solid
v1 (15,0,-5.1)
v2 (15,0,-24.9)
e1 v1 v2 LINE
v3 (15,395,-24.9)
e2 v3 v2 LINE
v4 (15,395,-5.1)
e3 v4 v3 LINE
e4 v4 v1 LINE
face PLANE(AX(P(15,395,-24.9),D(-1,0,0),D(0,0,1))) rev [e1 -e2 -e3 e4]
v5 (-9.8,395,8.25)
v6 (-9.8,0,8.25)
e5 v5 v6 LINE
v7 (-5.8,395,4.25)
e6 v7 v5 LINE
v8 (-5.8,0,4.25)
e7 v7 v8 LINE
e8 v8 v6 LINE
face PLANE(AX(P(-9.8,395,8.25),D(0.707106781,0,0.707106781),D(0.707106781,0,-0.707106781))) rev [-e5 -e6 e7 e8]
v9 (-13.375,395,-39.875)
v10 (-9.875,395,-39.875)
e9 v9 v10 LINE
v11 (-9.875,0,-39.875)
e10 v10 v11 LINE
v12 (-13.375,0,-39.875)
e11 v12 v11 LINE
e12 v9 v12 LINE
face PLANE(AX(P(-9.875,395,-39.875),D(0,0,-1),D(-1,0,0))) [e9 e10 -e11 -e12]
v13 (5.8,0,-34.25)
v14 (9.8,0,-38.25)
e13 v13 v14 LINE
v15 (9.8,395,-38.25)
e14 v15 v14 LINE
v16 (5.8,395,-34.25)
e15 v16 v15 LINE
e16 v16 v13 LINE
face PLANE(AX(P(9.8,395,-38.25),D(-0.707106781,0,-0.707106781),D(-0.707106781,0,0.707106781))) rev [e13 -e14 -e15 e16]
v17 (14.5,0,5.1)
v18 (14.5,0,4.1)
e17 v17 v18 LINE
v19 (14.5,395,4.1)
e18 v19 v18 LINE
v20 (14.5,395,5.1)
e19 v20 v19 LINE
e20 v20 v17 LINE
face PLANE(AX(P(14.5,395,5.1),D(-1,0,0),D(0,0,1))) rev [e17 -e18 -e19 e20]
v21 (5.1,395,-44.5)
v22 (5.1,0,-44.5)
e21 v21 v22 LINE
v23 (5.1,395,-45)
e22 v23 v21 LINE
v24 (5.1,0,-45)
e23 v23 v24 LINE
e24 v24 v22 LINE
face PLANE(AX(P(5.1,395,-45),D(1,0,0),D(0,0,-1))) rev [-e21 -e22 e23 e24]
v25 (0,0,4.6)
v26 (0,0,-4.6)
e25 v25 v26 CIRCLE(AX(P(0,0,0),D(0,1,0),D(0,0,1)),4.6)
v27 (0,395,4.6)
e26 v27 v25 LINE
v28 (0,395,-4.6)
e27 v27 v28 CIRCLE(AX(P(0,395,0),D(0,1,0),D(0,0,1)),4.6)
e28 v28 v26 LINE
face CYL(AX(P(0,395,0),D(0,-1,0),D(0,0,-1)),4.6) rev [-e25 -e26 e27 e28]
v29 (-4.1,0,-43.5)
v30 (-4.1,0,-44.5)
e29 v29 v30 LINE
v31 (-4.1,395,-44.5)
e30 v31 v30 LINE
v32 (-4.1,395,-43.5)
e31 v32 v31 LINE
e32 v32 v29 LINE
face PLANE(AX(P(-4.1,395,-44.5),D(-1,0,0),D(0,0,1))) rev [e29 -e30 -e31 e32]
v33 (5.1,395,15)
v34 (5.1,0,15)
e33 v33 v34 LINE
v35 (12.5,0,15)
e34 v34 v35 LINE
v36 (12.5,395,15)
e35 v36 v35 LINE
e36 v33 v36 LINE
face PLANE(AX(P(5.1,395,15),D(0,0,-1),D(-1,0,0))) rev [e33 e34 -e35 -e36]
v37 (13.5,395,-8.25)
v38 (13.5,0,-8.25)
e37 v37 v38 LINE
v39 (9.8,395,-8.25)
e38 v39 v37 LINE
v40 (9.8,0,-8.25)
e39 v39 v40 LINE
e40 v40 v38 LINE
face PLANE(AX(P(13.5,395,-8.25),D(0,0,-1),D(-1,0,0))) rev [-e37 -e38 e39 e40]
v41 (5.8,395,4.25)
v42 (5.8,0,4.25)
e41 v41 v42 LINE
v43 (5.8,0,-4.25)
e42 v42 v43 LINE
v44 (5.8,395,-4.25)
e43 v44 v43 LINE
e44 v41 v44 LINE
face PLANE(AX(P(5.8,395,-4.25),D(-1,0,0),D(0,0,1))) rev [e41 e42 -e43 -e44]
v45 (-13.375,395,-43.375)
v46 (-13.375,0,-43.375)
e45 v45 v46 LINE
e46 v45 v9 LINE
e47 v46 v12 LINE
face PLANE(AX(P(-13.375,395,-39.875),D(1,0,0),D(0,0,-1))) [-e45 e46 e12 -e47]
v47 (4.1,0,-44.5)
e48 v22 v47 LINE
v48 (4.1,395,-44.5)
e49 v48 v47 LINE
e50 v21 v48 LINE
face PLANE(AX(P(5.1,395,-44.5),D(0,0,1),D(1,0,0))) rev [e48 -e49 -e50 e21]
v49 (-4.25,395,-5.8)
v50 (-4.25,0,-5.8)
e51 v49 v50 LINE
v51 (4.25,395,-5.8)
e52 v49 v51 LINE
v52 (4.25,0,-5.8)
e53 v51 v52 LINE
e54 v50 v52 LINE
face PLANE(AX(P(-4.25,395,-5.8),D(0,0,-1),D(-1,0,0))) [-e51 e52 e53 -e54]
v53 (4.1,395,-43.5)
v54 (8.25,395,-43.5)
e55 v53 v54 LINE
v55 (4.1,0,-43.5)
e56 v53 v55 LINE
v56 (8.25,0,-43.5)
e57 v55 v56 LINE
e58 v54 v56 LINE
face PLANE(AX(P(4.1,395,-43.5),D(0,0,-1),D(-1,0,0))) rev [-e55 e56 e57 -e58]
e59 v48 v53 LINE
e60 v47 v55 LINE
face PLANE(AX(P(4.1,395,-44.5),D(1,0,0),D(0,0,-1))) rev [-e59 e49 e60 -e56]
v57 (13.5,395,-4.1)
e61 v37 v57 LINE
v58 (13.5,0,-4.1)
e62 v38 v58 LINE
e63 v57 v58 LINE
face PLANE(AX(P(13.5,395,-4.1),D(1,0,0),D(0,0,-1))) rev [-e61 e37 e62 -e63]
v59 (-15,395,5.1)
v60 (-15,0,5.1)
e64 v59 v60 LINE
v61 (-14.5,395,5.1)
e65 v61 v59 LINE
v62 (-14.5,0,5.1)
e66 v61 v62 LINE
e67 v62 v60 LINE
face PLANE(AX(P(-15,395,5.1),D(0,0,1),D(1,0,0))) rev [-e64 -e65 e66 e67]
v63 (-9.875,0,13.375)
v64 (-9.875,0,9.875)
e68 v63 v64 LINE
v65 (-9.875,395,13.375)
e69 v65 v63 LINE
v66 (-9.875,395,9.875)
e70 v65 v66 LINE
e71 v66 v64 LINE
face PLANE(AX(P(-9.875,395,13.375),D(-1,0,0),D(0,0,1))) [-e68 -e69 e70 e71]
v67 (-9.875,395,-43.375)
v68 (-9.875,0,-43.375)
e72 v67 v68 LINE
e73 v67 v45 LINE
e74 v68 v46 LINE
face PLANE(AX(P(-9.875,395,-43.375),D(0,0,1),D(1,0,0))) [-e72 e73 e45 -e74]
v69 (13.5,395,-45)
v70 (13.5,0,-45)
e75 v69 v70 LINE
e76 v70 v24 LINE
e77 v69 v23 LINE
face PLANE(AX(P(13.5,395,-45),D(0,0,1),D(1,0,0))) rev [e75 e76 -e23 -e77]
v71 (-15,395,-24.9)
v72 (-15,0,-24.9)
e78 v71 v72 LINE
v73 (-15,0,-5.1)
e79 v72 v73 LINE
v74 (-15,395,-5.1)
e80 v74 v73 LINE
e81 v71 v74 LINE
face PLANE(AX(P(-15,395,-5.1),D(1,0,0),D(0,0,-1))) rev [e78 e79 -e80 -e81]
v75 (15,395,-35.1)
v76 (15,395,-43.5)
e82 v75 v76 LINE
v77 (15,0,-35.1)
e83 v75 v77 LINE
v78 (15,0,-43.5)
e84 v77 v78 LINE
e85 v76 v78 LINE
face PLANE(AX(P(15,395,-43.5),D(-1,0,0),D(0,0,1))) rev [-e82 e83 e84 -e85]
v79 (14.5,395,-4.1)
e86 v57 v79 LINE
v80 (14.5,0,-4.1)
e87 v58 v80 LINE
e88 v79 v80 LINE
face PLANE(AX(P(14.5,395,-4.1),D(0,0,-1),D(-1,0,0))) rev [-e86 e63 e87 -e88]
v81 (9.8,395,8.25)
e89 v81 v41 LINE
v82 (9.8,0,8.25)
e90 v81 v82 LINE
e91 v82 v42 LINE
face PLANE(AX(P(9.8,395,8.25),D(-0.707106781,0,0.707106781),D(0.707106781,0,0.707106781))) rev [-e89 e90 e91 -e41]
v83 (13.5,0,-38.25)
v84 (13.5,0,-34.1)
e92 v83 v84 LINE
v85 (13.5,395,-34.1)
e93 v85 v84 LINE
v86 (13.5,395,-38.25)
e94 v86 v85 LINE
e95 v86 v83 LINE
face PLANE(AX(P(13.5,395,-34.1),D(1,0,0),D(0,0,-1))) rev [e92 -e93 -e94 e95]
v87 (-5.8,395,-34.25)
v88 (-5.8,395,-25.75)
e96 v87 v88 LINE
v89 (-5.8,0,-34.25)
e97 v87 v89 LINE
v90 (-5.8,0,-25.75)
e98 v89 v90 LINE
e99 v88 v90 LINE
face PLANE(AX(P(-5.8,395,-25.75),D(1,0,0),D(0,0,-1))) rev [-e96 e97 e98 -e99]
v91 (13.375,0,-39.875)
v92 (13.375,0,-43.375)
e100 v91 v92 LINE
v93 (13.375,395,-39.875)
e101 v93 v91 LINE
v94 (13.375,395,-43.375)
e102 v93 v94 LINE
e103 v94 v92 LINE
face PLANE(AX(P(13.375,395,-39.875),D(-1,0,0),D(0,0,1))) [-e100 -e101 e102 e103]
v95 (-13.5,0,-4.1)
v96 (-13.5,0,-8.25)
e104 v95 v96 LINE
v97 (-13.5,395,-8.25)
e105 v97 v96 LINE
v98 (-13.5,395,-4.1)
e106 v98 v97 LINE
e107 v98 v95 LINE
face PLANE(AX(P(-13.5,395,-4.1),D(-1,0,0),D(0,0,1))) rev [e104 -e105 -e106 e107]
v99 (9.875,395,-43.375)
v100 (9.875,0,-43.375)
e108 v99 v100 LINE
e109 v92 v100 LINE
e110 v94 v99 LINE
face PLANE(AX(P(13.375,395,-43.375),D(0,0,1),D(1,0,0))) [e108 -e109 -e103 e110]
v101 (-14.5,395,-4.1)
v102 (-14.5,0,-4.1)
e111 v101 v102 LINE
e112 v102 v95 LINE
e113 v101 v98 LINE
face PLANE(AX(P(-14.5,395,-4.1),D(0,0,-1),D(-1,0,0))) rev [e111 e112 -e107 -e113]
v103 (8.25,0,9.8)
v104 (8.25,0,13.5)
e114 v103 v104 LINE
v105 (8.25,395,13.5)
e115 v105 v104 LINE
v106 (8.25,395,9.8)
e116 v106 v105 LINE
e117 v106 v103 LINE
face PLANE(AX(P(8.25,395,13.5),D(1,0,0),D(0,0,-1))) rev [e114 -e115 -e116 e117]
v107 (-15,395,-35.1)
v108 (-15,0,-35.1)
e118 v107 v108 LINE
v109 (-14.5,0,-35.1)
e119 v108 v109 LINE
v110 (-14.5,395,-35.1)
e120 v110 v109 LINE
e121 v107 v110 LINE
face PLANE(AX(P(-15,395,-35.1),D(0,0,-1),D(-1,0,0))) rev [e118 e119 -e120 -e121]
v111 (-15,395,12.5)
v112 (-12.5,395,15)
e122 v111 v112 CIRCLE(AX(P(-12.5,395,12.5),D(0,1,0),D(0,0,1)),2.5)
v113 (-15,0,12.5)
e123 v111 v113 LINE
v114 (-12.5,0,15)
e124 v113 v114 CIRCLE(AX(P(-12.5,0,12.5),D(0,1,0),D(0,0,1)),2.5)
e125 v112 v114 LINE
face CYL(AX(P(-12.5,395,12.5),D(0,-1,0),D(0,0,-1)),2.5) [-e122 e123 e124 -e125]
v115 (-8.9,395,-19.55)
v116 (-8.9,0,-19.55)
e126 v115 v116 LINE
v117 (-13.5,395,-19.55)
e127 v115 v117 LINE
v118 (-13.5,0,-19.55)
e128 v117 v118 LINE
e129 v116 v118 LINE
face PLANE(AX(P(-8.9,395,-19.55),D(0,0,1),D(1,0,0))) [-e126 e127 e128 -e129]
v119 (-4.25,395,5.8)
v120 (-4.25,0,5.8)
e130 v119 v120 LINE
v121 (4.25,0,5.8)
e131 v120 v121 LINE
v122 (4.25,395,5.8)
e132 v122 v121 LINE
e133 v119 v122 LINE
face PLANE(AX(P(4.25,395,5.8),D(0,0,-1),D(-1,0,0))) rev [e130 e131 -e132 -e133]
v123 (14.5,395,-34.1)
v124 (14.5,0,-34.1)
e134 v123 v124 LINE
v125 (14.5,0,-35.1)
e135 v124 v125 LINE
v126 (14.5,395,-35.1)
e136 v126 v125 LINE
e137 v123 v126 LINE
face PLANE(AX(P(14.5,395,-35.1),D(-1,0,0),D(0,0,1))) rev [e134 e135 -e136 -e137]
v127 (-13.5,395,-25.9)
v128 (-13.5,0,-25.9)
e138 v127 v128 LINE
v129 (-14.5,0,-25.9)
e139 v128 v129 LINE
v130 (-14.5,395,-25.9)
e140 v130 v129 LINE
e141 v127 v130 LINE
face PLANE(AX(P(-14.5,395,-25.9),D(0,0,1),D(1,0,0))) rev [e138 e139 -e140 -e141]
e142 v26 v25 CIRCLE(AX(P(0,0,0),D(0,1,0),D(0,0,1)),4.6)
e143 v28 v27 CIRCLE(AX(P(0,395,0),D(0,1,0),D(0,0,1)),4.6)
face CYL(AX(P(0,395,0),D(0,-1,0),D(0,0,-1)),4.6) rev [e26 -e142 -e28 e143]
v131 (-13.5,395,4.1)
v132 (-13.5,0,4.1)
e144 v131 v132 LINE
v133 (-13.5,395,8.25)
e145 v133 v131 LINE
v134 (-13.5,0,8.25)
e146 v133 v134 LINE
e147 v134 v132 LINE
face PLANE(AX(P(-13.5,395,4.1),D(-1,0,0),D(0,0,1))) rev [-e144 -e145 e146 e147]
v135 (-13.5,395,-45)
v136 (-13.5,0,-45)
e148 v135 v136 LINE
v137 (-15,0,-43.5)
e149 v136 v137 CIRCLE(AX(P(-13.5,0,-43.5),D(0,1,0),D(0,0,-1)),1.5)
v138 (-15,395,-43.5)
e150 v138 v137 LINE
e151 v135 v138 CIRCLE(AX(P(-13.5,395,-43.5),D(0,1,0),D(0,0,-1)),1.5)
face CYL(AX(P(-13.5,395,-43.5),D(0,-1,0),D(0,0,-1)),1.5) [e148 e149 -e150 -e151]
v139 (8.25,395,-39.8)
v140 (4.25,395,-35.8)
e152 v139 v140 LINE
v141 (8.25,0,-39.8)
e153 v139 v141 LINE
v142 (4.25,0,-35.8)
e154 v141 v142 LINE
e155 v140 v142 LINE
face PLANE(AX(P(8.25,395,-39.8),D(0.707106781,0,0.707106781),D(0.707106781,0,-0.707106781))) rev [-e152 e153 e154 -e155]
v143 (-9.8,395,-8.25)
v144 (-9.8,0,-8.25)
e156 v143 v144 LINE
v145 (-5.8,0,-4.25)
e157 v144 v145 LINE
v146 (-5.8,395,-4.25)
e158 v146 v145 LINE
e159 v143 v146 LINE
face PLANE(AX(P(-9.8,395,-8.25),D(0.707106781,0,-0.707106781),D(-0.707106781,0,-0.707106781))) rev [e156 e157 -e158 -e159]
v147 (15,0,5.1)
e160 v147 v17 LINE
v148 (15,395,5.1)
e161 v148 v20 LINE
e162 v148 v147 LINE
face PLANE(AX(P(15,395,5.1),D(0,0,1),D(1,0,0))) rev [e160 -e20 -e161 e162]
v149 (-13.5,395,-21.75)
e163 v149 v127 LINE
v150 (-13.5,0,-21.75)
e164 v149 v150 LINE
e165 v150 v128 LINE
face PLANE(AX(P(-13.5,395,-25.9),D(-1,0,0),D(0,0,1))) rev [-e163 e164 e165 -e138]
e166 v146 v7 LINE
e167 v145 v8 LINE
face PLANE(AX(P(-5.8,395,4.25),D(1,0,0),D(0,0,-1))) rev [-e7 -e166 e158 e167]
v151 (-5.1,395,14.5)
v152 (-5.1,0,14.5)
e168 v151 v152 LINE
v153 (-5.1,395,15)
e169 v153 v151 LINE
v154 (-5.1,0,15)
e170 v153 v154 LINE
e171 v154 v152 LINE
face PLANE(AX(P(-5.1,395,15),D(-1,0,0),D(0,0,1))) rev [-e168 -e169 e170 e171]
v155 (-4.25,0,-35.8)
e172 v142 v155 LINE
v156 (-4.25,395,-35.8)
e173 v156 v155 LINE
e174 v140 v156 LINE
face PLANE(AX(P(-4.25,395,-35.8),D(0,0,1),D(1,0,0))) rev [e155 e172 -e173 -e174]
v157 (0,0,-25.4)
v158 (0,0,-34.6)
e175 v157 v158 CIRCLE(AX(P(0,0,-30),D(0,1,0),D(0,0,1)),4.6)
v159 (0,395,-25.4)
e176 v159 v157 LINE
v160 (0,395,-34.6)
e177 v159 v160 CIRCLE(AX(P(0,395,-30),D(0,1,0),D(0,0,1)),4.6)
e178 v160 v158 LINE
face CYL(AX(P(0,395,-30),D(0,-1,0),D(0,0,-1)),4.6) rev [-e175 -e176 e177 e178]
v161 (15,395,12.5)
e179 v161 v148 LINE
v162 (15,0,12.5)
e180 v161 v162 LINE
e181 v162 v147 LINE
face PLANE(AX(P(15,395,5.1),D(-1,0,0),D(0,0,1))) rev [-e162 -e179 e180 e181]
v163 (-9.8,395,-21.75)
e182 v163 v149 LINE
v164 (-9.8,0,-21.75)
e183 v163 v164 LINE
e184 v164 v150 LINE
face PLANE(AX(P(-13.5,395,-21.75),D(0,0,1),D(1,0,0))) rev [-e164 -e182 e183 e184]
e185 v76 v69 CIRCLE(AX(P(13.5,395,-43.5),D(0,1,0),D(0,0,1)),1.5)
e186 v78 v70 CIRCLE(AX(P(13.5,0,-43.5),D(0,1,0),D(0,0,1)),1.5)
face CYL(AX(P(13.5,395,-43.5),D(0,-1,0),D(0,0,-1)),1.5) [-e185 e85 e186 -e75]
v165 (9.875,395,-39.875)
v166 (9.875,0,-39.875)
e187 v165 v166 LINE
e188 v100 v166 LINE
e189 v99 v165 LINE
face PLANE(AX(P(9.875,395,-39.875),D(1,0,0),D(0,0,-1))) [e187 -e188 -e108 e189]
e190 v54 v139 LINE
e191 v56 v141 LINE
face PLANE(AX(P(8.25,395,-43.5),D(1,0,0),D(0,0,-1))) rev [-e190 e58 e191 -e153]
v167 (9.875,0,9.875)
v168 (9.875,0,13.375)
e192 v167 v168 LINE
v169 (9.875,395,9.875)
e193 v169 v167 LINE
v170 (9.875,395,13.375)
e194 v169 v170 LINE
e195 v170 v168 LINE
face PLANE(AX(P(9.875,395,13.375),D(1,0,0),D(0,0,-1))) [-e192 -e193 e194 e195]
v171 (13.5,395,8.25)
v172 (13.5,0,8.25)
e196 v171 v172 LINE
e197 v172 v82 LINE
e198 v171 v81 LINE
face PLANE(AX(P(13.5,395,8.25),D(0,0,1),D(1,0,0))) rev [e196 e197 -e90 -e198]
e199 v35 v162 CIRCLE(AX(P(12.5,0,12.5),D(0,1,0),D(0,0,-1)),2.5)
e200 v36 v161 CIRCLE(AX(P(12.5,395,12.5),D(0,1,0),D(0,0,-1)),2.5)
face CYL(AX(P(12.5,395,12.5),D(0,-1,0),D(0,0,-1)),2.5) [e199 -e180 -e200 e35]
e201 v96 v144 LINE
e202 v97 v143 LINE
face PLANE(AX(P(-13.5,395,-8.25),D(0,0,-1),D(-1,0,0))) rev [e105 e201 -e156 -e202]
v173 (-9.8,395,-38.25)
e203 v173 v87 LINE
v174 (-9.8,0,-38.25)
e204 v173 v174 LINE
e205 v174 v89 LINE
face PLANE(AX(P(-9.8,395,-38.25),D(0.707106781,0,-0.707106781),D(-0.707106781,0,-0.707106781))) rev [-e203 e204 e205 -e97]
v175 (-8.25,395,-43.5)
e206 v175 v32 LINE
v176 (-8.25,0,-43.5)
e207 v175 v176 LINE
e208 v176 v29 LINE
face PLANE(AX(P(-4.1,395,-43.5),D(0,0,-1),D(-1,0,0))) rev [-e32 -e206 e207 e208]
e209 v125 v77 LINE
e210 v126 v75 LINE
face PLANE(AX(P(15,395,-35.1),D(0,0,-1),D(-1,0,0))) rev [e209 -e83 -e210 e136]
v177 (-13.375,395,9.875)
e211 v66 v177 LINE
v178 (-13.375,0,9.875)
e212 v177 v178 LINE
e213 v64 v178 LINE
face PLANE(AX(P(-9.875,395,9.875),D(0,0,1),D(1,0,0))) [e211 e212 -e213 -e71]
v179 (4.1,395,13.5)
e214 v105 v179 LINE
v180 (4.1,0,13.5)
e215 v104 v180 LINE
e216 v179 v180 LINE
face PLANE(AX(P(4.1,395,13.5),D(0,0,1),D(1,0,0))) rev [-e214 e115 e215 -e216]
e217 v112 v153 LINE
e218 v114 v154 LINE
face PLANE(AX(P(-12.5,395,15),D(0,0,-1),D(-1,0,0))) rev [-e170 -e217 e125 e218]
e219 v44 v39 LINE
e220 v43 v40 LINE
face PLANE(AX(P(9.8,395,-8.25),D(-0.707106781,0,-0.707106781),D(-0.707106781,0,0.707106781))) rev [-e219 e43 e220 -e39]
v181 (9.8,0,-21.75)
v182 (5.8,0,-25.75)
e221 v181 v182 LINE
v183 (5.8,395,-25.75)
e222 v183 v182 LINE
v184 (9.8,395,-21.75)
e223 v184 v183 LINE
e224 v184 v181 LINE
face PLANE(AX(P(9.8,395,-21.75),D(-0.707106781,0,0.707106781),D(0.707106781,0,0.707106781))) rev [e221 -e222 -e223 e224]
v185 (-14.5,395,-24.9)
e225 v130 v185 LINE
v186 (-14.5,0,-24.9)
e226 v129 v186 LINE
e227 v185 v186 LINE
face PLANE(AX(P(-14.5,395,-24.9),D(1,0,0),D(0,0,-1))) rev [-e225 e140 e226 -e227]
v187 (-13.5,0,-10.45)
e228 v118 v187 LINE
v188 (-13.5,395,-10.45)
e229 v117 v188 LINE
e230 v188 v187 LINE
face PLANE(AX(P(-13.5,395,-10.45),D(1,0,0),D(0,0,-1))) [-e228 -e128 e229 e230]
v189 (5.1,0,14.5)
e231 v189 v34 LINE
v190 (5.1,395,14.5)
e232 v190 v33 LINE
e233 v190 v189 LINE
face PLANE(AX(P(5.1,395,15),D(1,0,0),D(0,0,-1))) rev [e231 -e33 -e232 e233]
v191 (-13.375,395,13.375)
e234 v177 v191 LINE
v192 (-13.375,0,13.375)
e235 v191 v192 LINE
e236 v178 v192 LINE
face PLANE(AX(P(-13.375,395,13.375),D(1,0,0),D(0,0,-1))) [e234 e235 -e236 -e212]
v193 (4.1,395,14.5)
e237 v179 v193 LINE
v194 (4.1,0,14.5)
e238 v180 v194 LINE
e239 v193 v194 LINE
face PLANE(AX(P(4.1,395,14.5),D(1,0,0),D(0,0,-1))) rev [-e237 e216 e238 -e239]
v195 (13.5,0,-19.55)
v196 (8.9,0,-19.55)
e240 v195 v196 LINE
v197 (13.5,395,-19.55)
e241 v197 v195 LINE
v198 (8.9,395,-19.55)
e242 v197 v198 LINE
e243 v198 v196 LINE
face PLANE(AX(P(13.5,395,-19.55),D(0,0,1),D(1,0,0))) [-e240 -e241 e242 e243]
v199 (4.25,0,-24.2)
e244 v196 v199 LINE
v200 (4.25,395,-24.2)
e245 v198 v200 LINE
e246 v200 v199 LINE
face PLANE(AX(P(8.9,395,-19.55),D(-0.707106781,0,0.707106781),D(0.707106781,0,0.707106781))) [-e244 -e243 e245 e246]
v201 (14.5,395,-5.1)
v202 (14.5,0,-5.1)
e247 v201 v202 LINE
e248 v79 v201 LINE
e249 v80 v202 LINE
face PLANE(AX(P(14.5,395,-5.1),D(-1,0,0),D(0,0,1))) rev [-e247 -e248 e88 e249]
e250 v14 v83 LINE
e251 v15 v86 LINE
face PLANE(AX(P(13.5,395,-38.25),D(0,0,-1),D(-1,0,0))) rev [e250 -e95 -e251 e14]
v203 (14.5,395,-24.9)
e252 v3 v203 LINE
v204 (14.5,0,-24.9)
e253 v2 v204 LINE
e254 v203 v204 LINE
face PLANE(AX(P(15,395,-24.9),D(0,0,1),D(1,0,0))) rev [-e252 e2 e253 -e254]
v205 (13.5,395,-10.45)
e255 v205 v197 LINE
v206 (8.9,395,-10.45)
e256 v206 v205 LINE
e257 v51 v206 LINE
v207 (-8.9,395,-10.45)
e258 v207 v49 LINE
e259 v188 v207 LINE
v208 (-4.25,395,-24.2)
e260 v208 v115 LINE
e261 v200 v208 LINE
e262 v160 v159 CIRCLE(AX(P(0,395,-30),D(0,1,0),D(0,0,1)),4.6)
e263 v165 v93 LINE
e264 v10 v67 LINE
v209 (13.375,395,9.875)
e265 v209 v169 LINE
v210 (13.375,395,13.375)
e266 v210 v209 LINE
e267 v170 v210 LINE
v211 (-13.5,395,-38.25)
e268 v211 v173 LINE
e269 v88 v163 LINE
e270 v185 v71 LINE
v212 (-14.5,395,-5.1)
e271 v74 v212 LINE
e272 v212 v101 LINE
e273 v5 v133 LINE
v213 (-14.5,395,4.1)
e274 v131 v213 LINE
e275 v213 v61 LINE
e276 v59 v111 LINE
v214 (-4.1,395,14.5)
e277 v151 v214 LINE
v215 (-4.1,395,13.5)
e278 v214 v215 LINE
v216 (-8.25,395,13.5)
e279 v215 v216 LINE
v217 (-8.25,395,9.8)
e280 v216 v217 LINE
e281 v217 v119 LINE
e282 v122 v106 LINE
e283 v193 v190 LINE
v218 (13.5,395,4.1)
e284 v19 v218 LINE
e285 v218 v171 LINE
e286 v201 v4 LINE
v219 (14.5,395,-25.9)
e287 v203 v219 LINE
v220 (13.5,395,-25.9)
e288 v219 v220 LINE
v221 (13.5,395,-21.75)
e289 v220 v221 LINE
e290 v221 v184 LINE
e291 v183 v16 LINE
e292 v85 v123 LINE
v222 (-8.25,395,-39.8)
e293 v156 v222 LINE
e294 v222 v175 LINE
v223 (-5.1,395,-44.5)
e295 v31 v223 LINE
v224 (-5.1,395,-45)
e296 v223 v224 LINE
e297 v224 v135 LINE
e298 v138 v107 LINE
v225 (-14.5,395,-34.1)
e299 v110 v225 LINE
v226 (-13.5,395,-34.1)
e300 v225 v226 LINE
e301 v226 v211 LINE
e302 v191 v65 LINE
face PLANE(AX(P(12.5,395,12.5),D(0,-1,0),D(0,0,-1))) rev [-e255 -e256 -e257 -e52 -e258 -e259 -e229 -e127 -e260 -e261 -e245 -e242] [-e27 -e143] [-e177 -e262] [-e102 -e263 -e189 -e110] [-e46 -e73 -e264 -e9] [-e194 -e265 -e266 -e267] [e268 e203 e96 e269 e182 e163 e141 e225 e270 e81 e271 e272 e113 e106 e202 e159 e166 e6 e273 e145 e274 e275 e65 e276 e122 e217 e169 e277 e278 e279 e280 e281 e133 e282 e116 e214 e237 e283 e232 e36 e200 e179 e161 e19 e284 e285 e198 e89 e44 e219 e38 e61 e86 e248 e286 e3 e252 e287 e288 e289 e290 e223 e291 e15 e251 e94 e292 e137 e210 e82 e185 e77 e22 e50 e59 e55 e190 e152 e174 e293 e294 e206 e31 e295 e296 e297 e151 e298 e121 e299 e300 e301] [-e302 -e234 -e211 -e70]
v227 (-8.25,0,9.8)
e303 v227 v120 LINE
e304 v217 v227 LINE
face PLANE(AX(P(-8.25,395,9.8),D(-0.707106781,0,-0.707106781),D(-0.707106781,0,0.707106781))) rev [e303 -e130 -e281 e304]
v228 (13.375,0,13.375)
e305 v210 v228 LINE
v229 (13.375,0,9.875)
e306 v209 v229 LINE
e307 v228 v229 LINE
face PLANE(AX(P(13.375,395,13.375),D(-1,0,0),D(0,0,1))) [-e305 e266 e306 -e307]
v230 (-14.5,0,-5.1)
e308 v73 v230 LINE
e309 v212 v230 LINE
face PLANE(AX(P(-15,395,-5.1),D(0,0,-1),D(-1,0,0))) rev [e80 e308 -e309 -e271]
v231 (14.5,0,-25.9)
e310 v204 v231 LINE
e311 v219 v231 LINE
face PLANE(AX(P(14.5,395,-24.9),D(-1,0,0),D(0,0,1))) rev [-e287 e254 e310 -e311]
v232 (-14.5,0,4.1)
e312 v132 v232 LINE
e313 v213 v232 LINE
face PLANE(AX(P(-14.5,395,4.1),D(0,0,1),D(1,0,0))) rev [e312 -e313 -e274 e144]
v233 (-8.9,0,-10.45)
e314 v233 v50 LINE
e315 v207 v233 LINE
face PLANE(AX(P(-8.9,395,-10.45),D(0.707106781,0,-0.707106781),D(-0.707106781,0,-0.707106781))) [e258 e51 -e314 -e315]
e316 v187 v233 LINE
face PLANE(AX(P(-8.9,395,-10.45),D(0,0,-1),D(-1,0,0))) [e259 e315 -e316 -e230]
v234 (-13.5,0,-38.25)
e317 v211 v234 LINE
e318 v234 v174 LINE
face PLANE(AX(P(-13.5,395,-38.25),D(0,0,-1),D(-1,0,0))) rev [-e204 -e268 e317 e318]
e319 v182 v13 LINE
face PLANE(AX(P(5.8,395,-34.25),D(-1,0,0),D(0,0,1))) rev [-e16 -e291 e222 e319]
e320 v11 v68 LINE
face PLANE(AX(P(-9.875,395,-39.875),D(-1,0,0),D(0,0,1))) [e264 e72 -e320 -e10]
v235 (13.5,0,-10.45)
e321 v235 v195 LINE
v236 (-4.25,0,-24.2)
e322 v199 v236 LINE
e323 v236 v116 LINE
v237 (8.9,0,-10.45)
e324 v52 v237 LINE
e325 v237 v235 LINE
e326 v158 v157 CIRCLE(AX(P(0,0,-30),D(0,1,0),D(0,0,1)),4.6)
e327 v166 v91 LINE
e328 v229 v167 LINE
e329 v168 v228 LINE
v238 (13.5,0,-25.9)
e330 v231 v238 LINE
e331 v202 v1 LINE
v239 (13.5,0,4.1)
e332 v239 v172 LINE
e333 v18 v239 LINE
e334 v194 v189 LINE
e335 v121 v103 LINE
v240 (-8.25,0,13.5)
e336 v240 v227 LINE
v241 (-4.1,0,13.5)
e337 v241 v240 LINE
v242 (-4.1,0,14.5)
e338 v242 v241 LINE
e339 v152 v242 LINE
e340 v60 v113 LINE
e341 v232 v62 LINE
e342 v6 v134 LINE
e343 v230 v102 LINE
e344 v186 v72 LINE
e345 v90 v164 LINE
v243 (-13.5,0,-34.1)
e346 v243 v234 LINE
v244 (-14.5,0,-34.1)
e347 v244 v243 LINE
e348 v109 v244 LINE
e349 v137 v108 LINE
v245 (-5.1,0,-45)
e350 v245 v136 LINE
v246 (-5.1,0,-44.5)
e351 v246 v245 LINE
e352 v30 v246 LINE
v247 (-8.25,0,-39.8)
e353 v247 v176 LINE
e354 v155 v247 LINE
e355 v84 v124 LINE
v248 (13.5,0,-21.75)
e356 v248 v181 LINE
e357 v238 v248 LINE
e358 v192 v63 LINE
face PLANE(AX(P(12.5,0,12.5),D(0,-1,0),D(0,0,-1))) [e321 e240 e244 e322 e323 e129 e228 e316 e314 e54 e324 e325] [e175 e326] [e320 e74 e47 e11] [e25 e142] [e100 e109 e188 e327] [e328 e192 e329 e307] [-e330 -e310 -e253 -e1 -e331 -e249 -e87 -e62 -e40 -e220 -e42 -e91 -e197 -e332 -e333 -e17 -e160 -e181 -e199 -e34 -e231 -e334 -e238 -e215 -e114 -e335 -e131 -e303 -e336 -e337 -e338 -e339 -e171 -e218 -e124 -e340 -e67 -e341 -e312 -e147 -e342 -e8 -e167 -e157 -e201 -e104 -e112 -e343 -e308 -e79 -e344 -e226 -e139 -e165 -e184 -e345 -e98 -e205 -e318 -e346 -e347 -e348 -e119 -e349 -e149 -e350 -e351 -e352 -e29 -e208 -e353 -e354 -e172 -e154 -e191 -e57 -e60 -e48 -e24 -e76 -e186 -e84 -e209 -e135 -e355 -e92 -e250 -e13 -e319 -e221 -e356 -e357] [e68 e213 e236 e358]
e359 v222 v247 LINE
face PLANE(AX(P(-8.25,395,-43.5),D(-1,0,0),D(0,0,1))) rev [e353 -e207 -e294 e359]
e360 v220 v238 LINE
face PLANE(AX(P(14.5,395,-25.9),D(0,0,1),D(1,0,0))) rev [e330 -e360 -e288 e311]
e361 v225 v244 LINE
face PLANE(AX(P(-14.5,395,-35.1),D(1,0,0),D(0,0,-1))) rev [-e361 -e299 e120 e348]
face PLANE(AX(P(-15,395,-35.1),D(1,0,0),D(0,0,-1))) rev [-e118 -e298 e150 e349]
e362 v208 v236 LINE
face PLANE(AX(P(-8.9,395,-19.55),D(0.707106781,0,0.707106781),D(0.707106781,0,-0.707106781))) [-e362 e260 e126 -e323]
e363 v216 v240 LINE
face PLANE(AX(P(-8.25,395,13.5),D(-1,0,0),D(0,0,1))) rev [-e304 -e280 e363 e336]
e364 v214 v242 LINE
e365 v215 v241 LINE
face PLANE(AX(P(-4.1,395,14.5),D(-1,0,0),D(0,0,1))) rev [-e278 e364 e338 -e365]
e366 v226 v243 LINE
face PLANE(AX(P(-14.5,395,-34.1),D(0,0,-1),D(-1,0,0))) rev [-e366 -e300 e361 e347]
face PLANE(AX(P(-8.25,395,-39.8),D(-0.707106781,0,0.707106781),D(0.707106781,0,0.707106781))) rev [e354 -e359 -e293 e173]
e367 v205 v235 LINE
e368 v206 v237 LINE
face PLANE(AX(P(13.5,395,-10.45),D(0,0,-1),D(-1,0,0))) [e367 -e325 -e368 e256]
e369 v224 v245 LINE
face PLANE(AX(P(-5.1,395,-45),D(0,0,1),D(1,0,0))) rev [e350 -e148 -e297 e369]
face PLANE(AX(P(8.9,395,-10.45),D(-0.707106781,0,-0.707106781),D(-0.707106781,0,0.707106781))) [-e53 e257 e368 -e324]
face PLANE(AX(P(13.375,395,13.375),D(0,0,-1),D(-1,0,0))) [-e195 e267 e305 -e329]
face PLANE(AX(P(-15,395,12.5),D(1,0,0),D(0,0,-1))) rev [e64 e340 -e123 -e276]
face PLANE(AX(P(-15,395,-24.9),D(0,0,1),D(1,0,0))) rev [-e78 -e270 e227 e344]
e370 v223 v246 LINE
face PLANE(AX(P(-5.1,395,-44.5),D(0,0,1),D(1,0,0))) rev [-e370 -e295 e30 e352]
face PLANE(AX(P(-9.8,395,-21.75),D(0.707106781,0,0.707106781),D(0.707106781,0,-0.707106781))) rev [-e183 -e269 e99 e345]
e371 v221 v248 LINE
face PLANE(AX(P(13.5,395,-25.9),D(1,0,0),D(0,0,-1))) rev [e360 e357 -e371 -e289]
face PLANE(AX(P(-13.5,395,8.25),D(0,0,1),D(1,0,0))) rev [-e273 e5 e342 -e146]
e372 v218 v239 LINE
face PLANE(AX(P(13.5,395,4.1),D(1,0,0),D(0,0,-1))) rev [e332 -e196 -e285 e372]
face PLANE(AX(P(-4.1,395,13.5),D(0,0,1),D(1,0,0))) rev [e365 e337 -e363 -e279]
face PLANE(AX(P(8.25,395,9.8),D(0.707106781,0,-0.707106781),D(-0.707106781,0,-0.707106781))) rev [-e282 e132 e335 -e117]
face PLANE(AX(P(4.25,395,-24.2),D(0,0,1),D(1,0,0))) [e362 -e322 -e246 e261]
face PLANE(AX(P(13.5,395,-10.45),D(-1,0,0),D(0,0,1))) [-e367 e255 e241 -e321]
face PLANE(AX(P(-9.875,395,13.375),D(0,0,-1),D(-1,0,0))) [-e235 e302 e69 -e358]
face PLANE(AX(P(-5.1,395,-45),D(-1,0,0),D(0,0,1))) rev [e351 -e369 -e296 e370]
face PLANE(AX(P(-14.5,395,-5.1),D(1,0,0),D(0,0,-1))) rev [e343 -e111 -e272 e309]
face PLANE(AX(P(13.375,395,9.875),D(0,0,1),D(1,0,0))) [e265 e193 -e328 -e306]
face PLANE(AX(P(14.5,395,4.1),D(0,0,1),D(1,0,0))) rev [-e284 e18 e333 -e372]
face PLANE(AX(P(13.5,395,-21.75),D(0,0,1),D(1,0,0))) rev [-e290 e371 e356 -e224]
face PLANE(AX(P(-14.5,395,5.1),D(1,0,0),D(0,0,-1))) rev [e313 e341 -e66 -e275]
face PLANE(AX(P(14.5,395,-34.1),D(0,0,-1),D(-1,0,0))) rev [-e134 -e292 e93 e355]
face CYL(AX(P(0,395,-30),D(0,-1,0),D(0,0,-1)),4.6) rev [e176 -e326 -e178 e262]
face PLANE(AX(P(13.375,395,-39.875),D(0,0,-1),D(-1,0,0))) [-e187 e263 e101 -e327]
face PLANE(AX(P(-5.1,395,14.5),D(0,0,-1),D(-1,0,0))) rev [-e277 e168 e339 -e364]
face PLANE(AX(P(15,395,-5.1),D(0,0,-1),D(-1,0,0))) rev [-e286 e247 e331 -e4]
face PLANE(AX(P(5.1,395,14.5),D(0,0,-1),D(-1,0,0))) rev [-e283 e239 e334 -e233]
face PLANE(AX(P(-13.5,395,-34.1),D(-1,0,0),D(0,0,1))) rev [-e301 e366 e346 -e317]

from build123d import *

# Parameters (mm, degrees)
SKETCH1_R                                = 4.6
SKETCH1_W                                = 3.5
SKETCH1_H                                = 3.5
ALUMINUM_PROFILE_30_X_60L_X_R2_5_1_DEPTH = 395


with BuildPart() as part:
    # Sketch1 → Aluminum profile 30 X 60L X R2.5(1) (new body)
    with BuildSketch(Plane(origin=(0, 0, 0), x_dir=(-1, 0, 0), z_dir=(0, 1, 0))):
        with BuildLine():
            Line((-5.1, 15), (-5.1, 14.5))
            Line((-5.1, 14.5), (-4.1, 14.5))
            Line((-4.1, 14.5), (-4.1, 13.5))
            Line((-4.1, 13.5), (-8.25, 13.5))
            Line((-8.25, 13.5), (-8.25, 9.8))
            Line((-8.25, 9.8), (-4.25, 5.8))
            Line((-4.25, 5.8), (4.25, 5.8))
            Line((4.25, 5.8), (8.25, 9.8))
            Line((8.25, 9.8), (8.25, 13.5))
            Line((8.25, 13.5), (4.1, 13.5))
            Line((4.1, 13.5), (4.1, 14.5))
            Line((4.1, 14.5), (5.1, 14.5))
            Line((5.1, 14.5), (5.1, 15))
            Line((5.1, 15), (12.5, 15))
            ThreePointArc((12.5, 15), (14.267766953, 14.267766953), (15, 12.5))
            Line((15, 12.5), (15, 5.1))
            Line((15, 5.1), (14.5, 5.1))
            Line((14.5, 5.1), (14.5, 4.1))
            Line((14.5, 4.1), (13.5, 4.1))
            Line((13.5, 4.1), (13.5, 8.25))
            Line((13.5, 8.25), (9.8, 8.25))
            Line((9.8, 8.25), (5.8, 4.25))
            Line((5.8, 4.25), (5.8, -4.25))
            Line((5.8, -4.25), (9.8, -8.25))
            Line((9.8, -8.25), (13.5, -8.25))
            Line((13.5, -8.25), (13.5, -4.1))
            Line((13.5, -4.1), (14.5, -4.1))
            Line((14.5, -4.1), (14.5, -5.1))
            Line((14.5, -5.1), (15, -5.1))
            Line((15, -5.1), (15, -24.9))
            Line((15, -24.9), (14.5, -24.9))
            Line((14.5, -24.9), (14.5, -25.9))
            Line((14.5, -25.9), (13.5, -25.9))
            Line((13.5, -25.9), (13.5, -21.75))
            Line((13.5, -21.75), (9.8, -21.75))
            Line((9.8, -21.75), (5.8, -25.75))
            Line((5.8, -25.75), (5.8, -34.25))
            Line((5.8, -34.25), (9.8, -38.25))
            Line((9.8, -38.25), (13.5, -38.25))
            Line((13.5, -38.25), (13.5, -34.1))
            Line((13.5, -34.1), (14.5, -34.1))
            Line((14.5, -34.1), (14.5, -35.1))
            Line((14.5, -35.1), (15, -35.1))
            Line((15, -35.1), (15, -43.5))
            ThreePointArc((15, -43.5), (14.560660172, -44.560660172), (13.5, -45))
            Line((13.5, -45), (5.1, -45))
            Line((5.1, -45), (5.1, -44.5))
            Line((5.1, -44.5), (4.1, -44.5))
            Line((4.1, -44.5), (4.1, -43.5))
            Line((4.1, -43.5), (8.25, -43.5))
            Line((8.25, -43.5), (8.25, -39.8))
            Line((8.25, -39.8), (4.25, -35.8))
            Line((4.25, -35.8), (-4.25, -35.8))
            Line((-4.25, -35.8), (-8.25, -39.8))
            Line((-8.25, -39.8), (-8.25, -43.5))
            Line((-8.25, -43.5), (-4.1, -43.5))
            Line((-4.1, -43.5), (-4.1, -44.5))
            Line((-4.1, -44.5), (-5.1, -44.5))
            Line((-5.1, -44.5), (-5.1, -45))
            Line((-5.1, -45), (-13.5, -45))
            ThreePointArc((-13.5, -45), (-14.560660172, -44.560660172), (-15, -43.5))
            Line((-15, -43.5), (-15, -35.1))
            Line((-15, -35.1), (-14.5, -35.1))
            Line((-14.5, -35.1), (-14.5, -34.1))
            Line((-14.5, -34.1), (-13.5, -34.1))
            Line((-13.5, -34.1), (-13.5, -38.25))
            Line((-13.5, -38.25), (-9.8, -38.25))
            Line((-9.8, -38.25), (-5.8, -34.25))
            Line((-5.8, -34.25), (-5.8, -25.75))
            Line((-5.8, -25.75), (-9.8, -21.75))
            Line((-9.8, -21.75), (-13.5, -21.75))
            Line((-13.5, -21.75), (-13.5, -25.9))
            Line((-13.5, -25.9), (-14.5, -25.9))
            Line((-14.5, -25.9), (-14.5, -24.9))
            Line((-14.5, -24.9), (-15, -24.9))
            Line((-15, -24.9), (-15, -5.1))
            Line((-15, -5.1), (-14.5, -5.1))
            Line((-14.5, -5.1), (-14.5, -4.1))
            Line((-14.5, -4.1), (-13.5, -4.1))
            Line((-13.5, -4.1), (-13.5, -8.25))
            Line((-13.5, -8.25), (-9.8, -8.25))
            Line((-9.8, -8.25), (-5.8, -4.25))
            Line((-5.8, -4.25), (-5.8, 4.25))
            Line((-5.8, 4.25), (-9.8, 8.25))
            Line((-9.8, 8.25), (-13.5, 8.25))
            Line((-13.5, 8.25), (-13.5, 4.1))
            Line((-13.5, 4.1), (-14.5, 4.1))
            Line((-14.5, 4.1), (-14.5, 5.1))
            Line((-14.5, 5.1), (-15, 5.1))
            Line((-15, 5.1), (-15, 12.5))
            ThreePointArc((-15, 12.5), (-14.267766953, 14.267766953), (-12.5, 15))
            Line((-12.5, 15), (-5.1, 15))
        make_face()
        Circle(SKETCH1_R, mode=Mode.SUBTRACT)
        with Locations((0, -30)):
            Circle(SKETCH1_R, mode=Mode.SUBTRACT)
        Polygon((8.9, -10.45), (4.25, -5.8), (-4.25, -5.8), (-8.9, -10.45), (-13.5, -10.45), (-13.5, -19.55), (-8.9, -19.55), (-4.25, -24.2), (4.25, -24.2), (8.9, -19.55), (13.5, -19.55), (13.5, -10.45), align=None, mode=Mode.SUBTRACT)
        with Locations((-11.625, 11.625)):
            Rectangle(SKETCH1_W, SKETCH1_H, mode=Mode.SUBTRACT)
        with Locations((11.625, 11.625)):
            Rectangle(SKETCH1_W, SKETCH1_H, mode=Mode.SUBTRACT)
        with Locations((-11.625, -41.625)):
            Rectangle(SKETCH1_W, SKETCH1_H, mode=Mode.SUBTRACT)
        with Locations((11.625, -41.625)):
            Rectangle(SKETCH1_W, SKETCH1_H, mode=Mode.SUBTRACT)
    extrude(amount=ALUMINUM_PROFILE_30_X_60L_X_R2_5_1_DEPTH)


solid = part.part
